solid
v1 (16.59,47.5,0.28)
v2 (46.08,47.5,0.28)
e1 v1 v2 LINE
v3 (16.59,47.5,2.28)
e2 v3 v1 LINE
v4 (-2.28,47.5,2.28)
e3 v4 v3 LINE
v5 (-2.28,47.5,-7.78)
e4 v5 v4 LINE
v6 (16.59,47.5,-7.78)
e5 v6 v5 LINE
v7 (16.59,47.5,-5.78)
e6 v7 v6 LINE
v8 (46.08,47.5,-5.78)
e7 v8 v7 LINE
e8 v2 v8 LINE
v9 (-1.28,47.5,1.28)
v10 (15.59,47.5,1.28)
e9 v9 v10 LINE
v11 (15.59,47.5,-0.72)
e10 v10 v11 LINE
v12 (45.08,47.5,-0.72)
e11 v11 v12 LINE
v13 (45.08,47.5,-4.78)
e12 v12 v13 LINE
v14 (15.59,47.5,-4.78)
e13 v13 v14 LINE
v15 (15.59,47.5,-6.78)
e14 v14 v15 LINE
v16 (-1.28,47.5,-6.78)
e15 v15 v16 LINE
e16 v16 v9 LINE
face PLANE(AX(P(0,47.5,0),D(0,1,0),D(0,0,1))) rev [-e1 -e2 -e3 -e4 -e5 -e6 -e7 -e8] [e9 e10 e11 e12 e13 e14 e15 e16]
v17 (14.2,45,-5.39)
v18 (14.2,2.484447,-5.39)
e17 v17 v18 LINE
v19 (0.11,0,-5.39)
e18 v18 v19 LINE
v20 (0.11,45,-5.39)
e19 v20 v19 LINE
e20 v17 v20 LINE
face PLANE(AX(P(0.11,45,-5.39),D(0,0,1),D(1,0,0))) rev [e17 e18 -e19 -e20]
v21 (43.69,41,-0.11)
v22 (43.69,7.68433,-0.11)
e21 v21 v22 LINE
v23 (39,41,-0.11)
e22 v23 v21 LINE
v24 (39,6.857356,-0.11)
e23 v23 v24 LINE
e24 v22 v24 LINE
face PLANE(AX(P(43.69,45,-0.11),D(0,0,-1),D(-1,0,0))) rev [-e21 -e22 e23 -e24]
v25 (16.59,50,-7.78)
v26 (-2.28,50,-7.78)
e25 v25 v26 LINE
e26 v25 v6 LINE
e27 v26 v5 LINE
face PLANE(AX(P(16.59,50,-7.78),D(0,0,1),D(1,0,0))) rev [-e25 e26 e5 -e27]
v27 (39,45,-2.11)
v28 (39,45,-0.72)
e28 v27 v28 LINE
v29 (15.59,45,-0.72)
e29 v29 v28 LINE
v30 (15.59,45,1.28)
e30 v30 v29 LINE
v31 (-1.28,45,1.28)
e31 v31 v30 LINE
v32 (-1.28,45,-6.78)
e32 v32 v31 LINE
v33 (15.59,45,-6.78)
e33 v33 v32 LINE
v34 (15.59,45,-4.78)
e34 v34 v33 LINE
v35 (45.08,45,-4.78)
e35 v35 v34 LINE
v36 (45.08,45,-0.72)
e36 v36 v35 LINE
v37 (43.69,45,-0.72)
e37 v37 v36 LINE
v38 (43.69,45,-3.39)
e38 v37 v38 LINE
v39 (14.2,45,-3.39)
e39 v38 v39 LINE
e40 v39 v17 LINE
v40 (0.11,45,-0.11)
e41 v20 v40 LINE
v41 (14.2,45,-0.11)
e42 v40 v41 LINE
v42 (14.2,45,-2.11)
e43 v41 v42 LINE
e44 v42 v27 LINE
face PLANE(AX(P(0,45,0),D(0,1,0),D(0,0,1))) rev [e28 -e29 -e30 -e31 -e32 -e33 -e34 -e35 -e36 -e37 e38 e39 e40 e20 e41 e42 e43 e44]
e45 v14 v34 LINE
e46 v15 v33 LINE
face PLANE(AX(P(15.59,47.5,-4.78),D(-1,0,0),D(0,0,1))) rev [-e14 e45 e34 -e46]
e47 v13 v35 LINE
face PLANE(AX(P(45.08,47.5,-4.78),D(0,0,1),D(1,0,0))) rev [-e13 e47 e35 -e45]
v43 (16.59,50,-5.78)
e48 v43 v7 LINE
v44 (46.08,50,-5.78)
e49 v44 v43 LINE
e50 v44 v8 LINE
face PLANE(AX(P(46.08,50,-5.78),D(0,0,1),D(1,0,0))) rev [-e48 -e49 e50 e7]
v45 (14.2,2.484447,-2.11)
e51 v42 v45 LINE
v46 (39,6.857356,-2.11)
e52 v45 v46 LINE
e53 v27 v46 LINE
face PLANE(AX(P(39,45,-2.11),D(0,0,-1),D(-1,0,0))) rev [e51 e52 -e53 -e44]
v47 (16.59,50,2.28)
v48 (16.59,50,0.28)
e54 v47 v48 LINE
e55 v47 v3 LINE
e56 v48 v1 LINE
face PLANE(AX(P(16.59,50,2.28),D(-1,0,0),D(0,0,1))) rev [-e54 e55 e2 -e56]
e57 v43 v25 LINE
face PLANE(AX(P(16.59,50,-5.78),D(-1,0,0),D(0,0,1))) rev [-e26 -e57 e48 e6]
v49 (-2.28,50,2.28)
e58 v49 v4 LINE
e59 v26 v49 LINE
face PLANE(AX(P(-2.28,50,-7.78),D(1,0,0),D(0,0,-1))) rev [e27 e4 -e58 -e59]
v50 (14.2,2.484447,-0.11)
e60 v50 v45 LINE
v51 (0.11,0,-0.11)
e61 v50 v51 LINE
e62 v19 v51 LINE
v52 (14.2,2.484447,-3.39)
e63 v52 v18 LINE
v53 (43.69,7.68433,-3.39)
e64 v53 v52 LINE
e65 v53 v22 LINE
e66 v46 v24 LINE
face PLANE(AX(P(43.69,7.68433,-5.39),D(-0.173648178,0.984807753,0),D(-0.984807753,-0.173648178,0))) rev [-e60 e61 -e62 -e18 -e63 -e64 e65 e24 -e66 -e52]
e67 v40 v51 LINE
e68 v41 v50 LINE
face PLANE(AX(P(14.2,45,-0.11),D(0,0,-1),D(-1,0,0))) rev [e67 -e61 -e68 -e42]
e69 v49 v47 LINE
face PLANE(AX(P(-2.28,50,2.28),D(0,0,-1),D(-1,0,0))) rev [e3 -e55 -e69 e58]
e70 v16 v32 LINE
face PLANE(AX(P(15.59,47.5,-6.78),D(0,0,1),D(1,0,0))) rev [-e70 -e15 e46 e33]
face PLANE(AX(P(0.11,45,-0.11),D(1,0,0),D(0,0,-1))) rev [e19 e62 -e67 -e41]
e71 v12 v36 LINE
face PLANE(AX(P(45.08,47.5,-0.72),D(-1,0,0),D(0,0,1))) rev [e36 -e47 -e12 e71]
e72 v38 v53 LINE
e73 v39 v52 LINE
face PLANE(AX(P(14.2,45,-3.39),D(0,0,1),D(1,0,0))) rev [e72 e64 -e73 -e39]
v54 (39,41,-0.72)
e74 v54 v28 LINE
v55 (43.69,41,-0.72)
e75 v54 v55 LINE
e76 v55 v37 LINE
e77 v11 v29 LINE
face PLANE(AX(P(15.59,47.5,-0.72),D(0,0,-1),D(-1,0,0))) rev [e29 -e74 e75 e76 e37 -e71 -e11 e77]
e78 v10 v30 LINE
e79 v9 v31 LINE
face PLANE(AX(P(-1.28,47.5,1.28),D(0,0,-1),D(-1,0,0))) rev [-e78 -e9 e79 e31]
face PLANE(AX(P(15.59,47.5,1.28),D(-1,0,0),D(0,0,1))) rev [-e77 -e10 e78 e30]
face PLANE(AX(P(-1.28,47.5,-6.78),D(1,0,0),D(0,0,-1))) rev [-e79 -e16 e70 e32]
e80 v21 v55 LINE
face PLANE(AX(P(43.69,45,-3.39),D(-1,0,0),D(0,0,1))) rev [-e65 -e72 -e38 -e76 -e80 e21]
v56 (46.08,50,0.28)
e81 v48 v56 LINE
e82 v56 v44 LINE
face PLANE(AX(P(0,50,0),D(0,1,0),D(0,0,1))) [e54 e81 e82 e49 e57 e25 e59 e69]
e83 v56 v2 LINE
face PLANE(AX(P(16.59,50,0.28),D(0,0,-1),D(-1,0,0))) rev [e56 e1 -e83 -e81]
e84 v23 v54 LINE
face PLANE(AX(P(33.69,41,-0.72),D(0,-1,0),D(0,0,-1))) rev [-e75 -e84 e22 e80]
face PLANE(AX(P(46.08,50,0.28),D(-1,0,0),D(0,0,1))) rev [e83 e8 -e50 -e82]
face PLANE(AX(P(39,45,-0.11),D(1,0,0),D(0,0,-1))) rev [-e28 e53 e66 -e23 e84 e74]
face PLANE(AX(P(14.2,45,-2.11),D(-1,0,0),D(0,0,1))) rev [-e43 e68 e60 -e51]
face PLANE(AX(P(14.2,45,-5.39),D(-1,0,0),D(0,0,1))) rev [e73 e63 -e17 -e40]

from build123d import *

# Parameters (mm, degrees)
BOSS_EXTRUDE1_DEPTH = 45
CUT_EXTRUDE1_DEPTH  = 63.941993137
BOSS_EXTRUDE2_DEPTH = 2.5
BOSS_EXTRUDE3_DEPTH = 2.5
SKETCH6_W           = 0.61
SKETCH6_H           = 4
CUT_EXTRUDE2_DEPTH  = 10


with BuildPart() as part:
    # Sketch2 → Boss-Extrude1 (new body)
    with BuildSketch(Plane(origin=(0, 0, 0), x_dir=(1, 0, 0), z_dir=(0, 1, 0))):
        Polygon((0.11, 0.11), (0.11, 5.39), (14.2, 5.39), (14.2, 3.39), (43.69, 3.39), (43.69, 0.11), (39, 0.11), (39, 2.11), (14.2, 2.11), (14.2, 0.11), align=None)
    extrude(amount=BOSS_EXTRUDE1_DEPTH)

    # Sketch3 → Cut-Extrude1 (cut, through all)
    with BuildSketch(Plane.XY.offset(-0.11)):
        Polygon((0.11, 0), (43.69, 0), (43.69, 7.684329819), align=None)
    extrude(amount=-CUT_EXTRUDE1_DEPTH, mode=Mode.SUBTRACT)

    # Sketch4 → Boss-Extrude2 (add)
    with BuildSketch(Plane(origin=(0, 45, 0), x_dir=(1, 0, 0), z_dir=(0, 1, 0))):
        Polygon((-1.28, 6.78), (-1.28, -1.28), (15.59, -1.28), (15.59, 0.72), (45.08, 0.72), (45.08, 4.78), (15.59, 4.78), (15.59, 6.78), align=None)
    extrude(amount=BOSS_EXTRUDE2_DEPTH)

    # Sketch5 → Boss-Extrude3 (add)
    with BuildSketch(Plane(origin=(0, 47.5, 0), x_dir=(1, 0, 0), z_dir=(0, 1, 0))):
        Polygon((46.08, -0.28), (46.08, 5.78), (16.59, 5.78), (16.59, 7.78), (-2.28, 7.78), (-2.28, -2.28), (16.59, -2.28), (16.59, -0.28), align=None)
    extrude(amount=BOSS_EXTRUDE3_DEPTH)

    # Sketch6 → Cut-Extrude2 (cut)
    with BuildSketch(Plane(origin=(43.69, 0, 0), x_dir=(0, 0, -1), z_dir=(1, 0, 0))):
        with Locations((0.415, 43)):
            Rectangle(SKETCH6_W, SKETCH6_H)
    extrude(amount=-CUT_EXTRUDE2_DEPTH, mode=Mode.SUBTRACT)


solid = part.part
